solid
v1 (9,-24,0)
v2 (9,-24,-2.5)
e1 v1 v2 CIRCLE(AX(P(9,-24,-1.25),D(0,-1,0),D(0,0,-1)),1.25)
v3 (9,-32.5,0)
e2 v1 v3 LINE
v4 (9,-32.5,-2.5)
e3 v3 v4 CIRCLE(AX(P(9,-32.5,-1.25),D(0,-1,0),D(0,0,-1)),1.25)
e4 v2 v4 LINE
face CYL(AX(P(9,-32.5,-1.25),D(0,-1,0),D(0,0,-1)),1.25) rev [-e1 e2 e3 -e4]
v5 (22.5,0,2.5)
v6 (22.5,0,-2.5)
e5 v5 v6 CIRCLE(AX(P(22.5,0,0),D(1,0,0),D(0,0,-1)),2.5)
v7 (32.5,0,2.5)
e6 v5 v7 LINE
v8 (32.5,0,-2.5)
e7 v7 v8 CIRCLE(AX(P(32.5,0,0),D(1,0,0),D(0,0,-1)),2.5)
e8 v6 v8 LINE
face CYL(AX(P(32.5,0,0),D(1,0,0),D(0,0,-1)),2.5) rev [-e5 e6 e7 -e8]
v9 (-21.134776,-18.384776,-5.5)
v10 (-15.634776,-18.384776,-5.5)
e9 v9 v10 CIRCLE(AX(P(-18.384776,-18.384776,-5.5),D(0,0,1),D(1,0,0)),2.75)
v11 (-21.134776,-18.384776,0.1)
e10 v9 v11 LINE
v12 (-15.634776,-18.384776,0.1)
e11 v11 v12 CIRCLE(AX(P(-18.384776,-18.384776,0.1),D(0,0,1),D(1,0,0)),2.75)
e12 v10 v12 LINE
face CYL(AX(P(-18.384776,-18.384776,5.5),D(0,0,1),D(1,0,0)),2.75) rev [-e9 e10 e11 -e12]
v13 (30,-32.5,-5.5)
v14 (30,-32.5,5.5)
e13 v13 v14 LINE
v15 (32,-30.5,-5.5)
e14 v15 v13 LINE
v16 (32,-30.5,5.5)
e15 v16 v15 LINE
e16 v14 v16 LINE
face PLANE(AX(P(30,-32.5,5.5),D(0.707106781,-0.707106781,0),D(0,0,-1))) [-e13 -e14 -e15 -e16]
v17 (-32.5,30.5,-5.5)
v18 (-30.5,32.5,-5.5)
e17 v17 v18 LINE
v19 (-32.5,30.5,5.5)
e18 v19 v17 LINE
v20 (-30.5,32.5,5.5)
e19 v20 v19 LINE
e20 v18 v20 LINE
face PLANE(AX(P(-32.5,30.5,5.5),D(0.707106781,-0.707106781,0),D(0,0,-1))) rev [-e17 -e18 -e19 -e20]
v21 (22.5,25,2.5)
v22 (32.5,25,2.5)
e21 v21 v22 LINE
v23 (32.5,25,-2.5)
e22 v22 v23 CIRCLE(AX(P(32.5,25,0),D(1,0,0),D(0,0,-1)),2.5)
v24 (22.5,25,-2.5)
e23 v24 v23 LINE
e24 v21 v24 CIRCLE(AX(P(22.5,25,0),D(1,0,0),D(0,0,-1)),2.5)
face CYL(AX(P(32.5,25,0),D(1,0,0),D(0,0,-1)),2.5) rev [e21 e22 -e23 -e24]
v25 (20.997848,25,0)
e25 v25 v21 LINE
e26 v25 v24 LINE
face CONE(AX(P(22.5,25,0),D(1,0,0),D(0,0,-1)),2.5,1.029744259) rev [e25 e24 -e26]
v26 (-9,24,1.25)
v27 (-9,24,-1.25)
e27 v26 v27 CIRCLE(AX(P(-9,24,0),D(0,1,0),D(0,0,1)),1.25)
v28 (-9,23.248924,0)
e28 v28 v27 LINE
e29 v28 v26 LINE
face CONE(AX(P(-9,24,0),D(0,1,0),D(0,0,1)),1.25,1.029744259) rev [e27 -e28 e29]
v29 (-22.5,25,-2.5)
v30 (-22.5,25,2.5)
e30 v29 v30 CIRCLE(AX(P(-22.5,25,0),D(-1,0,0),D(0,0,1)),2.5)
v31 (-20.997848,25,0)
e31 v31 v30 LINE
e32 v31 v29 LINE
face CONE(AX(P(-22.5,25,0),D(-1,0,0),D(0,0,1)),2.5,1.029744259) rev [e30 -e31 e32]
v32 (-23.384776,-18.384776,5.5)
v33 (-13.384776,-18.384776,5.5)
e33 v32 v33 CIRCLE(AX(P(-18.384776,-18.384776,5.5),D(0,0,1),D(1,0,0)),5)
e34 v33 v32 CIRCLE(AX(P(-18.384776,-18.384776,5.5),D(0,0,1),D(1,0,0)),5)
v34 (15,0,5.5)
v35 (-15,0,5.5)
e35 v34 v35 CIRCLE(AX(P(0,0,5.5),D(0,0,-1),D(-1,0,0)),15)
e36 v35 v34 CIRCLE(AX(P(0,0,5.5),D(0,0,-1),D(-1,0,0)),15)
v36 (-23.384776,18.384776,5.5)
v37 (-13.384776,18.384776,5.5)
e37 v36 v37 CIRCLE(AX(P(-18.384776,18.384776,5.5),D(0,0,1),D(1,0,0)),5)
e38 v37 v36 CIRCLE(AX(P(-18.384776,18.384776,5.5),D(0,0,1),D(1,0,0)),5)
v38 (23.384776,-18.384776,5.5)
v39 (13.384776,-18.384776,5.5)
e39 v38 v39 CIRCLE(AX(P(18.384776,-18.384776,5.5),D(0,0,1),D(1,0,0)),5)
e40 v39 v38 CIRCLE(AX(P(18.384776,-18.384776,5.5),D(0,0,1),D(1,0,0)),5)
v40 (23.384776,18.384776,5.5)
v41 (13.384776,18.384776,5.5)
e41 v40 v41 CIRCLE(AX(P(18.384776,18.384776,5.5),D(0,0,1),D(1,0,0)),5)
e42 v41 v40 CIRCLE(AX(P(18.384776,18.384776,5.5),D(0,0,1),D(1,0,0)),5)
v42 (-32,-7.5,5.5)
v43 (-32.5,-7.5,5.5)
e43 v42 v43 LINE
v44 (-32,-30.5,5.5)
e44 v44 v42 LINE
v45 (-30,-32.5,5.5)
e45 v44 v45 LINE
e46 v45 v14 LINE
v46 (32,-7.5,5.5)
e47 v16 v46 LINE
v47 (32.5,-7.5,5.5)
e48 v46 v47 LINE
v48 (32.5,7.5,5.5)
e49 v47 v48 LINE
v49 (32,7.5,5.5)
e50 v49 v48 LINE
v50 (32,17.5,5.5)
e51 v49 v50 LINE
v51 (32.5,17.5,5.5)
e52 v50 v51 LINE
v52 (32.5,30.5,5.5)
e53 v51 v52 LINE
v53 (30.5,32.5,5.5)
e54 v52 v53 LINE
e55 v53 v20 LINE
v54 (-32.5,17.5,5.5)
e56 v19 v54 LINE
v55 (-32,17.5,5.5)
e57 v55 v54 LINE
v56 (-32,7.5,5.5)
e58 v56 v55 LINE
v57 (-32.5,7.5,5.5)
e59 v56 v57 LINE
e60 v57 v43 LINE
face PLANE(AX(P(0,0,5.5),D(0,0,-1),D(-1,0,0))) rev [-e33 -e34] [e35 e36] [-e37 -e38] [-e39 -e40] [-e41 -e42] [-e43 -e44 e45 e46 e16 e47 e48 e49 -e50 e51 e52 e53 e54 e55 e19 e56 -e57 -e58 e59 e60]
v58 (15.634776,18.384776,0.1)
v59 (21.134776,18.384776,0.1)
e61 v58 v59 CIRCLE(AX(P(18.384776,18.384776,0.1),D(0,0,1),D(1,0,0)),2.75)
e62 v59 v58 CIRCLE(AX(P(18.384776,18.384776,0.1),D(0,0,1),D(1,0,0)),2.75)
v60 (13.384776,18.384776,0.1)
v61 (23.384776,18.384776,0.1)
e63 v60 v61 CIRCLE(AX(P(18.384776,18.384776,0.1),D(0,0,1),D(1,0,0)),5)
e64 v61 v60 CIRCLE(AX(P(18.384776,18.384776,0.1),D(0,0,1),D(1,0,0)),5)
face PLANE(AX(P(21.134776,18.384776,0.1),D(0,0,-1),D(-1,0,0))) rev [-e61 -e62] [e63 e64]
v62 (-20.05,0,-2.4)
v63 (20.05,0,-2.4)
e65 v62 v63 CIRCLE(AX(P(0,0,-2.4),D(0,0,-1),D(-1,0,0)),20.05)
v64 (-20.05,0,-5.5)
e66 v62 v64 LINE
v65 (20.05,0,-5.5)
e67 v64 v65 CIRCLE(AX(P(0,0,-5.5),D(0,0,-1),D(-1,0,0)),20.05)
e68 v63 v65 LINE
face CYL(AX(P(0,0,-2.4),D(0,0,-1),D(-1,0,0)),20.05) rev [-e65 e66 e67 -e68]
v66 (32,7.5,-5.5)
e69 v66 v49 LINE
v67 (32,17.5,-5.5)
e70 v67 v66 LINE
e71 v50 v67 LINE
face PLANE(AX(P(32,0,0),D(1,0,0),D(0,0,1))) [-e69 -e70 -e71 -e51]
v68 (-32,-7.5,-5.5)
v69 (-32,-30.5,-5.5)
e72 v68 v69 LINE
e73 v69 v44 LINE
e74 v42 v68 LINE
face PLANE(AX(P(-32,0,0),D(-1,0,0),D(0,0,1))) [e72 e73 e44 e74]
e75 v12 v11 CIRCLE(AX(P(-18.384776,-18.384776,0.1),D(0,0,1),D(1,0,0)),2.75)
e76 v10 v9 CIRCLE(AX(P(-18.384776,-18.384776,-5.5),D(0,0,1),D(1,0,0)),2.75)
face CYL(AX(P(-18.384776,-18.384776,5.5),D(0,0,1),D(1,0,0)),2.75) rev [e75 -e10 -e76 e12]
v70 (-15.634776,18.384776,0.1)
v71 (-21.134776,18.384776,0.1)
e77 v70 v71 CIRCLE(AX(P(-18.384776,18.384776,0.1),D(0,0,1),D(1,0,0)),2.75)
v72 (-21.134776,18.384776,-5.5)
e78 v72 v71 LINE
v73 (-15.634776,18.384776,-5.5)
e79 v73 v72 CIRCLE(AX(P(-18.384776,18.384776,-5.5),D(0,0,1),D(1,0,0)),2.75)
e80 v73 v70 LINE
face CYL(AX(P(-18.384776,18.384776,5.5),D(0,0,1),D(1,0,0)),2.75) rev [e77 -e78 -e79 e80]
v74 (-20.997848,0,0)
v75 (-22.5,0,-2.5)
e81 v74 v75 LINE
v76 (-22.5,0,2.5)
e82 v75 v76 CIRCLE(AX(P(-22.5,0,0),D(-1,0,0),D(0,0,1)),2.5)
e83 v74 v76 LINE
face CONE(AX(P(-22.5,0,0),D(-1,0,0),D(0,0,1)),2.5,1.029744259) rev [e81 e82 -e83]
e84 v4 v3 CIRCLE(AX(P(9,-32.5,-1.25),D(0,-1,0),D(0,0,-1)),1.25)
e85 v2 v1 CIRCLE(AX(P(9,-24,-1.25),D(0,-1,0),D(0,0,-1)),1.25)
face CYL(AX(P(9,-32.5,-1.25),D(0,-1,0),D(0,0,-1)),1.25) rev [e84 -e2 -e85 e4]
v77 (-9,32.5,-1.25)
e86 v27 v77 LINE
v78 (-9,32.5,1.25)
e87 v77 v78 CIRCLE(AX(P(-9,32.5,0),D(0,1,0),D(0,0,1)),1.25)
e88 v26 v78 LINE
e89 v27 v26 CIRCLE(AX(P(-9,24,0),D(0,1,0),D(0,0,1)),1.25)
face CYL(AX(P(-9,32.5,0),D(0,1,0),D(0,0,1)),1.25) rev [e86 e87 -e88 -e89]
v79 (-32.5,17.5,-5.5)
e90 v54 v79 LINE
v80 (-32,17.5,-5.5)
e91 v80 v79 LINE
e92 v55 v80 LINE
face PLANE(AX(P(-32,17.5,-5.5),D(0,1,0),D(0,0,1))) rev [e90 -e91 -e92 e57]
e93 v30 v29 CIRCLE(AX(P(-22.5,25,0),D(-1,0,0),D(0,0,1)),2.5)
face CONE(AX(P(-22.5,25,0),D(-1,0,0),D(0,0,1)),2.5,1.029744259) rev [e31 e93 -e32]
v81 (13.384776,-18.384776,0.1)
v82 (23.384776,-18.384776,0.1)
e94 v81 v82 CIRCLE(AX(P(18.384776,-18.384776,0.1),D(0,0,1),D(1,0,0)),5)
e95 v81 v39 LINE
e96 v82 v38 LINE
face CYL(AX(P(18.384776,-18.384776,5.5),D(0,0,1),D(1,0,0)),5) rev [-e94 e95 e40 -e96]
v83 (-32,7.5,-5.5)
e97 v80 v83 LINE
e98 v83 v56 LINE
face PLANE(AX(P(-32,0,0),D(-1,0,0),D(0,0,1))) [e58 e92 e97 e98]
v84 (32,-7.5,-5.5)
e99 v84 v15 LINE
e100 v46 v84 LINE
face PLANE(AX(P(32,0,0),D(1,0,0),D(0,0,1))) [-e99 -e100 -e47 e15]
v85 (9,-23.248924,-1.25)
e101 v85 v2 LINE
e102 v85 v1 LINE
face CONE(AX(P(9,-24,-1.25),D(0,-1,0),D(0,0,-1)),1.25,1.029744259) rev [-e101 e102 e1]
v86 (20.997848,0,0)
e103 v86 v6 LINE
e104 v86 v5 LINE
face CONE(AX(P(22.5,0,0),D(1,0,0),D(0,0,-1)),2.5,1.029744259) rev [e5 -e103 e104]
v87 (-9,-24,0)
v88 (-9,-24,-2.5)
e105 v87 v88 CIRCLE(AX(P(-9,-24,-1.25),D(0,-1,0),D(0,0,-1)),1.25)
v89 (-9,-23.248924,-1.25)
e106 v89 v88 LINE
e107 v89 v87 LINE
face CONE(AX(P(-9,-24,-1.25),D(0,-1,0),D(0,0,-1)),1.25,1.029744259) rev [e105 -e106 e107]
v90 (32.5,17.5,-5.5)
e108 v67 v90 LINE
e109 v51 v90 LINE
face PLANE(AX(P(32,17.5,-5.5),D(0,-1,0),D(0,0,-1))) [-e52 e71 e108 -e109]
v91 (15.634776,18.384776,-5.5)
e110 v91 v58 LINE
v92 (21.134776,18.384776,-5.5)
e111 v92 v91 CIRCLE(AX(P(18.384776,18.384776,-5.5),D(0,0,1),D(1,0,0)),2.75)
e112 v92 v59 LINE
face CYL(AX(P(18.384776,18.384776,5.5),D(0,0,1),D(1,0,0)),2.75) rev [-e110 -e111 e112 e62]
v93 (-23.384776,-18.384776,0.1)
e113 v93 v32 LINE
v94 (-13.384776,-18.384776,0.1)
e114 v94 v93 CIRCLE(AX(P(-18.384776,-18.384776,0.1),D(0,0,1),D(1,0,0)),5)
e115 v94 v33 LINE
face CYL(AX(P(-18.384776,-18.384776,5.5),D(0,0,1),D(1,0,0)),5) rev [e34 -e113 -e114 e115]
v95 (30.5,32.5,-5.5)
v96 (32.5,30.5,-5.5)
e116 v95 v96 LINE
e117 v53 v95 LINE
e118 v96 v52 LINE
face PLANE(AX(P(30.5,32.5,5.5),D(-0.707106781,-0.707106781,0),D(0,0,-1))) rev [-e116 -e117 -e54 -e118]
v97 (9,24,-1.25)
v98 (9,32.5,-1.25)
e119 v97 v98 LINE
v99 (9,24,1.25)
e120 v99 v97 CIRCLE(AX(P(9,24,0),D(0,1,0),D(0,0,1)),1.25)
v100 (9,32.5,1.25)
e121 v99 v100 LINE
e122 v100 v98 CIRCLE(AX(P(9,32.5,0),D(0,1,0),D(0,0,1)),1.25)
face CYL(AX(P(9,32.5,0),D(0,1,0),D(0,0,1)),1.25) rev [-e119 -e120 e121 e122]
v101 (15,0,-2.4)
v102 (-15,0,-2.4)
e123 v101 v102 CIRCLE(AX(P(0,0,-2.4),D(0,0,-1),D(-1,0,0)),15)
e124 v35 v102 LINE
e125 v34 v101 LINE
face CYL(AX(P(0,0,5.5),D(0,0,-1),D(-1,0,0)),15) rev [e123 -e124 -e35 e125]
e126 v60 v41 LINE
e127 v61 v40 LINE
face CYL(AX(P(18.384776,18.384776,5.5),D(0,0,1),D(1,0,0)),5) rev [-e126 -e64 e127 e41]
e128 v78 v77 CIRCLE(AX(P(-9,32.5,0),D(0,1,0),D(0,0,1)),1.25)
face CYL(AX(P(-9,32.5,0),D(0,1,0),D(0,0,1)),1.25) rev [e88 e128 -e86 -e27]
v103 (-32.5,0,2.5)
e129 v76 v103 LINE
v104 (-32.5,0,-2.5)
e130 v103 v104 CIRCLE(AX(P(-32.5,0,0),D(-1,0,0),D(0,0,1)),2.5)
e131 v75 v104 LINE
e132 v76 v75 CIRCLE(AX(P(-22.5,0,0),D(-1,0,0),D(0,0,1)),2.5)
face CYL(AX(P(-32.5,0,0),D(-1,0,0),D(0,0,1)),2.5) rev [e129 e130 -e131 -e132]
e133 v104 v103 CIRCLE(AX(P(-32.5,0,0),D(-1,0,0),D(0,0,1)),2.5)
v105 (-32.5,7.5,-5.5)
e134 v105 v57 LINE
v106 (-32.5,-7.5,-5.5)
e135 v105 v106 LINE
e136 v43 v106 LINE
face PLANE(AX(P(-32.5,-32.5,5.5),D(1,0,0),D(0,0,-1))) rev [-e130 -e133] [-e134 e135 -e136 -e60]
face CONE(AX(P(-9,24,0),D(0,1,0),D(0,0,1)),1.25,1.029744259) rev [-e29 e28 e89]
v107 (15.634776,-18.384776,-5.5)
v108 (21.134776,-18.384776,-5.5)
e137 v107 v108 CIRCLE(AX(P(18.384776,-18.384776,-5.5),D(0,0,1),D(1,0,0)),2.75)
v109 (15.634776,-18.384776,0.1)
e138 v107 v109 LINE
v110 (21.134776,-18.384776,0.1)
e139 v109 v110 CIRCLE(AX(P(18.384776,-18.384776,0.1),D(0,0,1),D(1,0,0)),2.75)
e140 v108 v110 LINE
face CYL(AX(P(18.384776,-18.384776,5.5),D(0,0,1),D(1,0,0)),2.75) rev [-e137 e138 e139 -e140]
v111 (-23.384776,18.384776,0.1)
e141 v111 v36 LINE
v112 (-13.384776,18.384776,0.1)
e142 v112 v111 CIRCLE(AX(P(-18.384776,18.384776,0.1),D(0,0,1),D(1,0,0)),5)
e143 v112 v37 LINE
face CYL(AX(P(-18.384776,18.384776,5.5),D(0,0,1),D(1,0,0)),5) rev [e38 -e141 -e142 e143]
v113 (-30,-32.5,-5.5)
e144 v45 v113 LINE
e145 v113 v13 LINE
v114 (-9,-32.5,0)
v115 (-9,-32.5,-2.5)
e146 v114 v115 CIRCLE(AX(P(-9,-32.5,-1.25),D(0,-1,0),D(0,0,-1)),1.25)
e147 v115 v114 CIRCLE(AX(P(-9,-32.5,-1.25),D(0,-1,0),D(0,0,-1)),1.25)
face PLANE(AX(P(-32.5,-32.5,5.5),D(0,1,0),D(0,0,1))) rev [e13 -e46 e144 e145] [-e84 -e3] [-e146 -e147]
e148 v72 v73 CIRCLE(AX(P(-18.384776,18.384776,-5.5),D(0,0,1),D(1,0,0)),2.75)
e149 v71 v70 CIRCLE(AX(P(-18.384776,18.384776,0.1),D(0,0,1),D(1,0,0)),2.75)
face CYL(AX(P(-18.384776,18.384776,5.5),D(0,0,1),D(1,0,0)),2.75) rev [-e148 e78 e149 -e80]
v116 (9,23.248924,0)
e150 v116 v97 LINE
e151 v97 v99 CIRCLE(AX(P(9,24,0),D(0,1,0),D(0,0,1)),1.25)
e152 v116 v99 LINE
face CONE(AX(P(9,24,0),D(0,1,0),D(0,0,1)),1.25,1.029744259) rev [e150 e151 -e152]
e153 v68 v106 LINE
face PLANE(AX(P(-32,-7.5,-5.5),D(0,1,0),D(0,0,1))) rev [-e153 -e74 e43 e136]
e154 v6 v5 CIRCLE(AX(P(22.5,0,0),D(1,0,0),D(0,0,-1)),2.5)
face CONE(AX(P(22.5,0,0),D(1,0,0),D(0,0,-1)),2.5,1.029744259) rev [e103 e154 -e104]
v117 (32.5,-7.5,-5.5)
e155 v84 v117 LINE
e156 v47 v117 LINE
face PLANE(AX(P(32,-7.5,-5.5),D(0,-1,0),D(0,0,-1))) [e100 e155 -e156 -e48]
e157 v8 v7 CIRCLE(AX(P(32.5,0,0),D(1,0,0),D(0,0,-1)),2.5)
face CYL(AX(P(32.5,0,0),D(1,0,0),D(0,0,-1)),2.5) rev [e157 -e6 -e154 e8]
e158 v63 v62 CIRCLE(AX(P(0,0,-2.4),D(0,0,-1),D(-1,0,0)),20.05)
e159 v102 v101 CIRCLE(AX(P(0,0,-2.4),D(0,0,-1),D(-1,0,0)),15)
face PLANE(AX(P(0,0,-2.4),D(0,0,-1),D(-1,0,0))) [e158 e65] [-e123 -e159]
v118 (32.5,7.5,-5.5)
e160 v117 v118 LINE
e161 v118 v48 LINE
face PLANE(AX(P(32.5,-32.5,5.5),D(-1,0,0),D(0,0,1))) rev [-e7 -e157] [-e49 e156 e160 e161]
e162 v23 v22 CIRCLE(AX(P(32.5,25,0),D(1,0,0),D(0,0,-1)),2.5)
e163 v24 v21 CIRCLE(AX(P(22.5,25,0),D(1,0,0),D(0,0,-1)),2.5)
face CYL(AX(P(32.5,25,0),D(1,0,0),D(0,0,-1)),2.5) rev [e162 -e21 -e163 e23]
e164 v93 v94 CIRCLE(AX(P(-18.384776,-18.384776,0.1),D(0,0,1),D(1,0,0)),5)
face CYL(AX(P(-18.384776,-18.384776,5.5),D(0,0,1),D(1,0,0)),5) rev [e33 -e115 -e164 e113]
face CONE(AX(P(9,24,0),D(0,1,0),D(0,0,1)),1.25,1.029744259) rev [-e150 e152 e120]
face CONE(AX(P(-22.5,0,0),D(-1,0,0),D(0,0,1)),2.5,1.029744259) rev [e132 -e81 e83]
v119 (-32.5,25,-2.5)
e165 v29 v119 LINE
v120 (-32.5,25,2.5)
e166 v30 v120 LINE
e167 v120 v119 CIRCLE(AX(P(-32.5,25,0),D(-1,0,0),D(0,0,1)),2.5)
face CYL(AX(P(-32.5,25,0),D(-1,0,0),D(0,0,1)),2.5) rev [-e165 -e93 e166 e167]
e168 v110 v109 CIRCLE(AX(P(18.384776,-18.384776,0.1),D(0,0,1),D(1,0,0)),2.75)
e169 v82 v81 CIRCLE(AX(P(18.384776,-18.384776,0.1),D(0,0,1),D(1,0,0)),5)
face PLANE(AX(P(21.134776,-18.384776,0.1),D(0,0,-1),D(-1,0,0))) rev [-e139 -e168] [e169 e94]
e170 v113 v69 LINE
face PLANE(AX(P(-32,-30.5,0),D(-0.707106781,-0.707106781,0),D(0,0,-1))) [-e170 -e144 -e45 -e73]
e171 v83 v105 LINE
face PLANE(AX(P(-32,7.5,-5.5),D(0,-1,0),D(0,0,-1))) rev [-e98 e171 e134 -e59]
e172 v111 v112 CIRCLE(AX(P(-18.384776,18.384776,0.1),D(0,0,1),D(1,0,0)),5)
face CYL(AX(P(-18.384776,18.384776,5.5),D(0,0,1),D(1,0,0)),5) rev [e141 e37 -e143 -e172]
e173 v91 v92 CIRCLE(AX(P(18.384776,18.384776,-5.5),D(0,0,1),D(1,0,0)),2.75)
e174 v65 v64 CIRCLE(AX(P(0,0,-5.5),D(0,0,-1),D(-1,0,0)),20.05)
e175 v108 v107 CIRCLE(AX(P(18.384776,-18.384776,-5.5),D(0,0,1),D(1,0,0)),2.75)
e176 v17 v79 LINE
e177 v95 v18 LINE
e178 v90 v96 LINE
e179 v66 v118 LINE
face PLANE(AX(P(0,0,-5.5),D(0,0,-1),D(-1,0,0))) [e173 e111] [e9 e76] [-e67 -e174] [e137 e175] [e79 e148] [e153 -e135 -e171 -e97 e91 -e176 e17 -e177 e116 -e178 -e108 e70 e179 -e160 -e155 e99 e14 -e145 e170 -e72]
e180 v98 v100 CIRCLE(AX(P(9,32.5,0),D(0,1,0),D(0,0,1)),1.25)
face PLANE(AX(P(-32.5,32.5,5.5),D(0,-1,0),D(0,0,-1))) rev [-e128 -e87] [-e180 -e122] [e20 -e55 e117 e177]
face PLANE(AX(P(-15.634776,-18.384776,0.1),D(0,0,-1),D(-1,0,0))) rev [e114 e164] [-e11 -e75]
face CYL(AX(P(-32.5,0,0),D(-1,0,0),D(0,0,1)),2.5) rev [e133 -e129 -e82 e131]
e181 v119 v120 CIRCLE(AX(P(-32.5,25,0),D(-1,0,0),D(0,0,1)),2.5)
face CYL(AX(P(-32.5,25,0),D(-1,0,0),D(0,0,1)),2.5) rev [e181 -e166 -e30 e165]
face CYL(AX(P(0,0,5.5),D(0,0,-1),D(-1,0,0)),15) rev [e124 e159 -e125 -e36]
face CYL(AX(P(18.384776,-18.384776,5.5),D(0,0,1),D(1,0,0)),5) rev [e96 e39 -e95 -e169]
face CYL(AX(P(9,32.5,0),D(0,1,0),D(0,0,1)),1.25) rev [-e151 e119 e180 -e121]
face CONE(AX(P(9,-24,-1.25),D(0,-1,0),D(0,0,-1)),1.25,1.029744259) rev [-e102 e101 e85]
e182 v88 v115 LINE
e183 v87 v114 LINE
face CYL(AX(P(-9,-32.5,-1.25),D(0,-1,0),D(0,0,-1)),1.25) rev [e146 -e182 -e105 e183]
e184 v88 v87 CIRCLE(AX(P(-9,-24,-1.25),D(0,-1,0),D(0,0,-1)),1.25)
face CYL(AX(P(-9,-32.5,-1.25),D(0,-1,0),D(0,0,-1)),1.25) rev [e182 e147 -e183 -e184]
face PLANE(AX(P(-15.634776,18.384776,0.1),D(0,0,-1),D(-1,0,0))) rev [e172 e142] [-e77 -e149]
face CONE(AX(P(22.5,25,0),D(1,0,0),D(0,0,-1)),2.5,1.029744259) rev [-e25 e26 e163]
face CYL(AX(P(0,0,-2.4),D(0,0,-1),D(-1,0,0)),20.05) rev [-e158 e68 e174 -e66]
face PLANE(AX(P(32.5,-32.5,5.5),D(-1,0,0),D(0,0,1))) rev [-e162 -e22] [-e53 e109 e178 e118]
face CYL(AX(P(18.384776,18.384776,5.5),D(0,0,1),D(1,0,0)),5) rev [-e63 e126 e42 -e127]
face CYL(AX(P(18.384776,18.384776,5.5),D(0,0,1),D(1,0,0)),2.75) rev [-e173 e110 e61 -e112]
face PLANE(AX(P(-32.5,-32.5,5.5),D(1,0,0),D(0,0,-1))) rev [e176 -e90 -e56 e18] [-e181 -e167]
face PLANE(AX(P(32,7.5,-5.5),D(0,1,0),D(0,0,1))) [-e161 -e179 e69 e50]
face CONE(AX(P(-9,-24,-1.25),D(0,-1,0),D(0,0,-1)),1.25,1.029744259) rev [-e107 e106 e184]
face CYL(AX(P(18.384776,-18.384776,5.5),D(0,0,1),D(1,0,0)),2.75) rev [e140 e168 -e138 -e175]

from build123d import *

# Parameters (mm, degrees)
SKETCH_1_W                   = 65
SKETCH_1_H                   = 65
EXTRUDE_1_DEPTH              = 5.5
SKETCH_3_R                   = 20.05
CUT_EXTRUDE_1_DEPTH          = 3.1
SKETCH_4_R                   = 15
CUT_EXTRUDE_2_DEPTH          = 47.635930354
HOLE_WIZARD_M5_1_D           = 5.5
HOLE_WIZARD_M5_1_CBORE_D     = 10
HOLE_WIZARD_M5_1_CBORE_DEPTH = 5.4
HOLE_WIZARD_M6_1_AT_2_COUNT  = 2
HOLE_WIZARD_M6_1_AT_2_PITCH  = 25
SKETCH_12_W                  = 11
SKETCH_12_H                  = 10
SKETCH_12_H_2                = 25
CUT_EXTRUDE_3_DEPTH          = 0.5
CHAMFER_1_SIZE               = 2
HOLE_WIZARD_M3_2_D           = 2.5
HOLE_WIZARD_M3_2_DEPTH       = 8.5
HOLE_WIZARD_M3_2_TIP         = 0.751075774
HOLE_WIZARD_M3_3_D           = 2.5
HOLE_WIZARD_M3_3_DEPTH       = 8.5
HOLE_WIZARD_M3_3_TIP         = 0.751075774


with BuildPart() as part:
    # 草图1 → 凸台-拉伸1 (new, symmetric)
    with BuildSketch(Plane.XY):
        Rectangle(SKETCH_1_W, SKETCH_1_H)
    extrude(amount=EXTRUDE_1_DEPTH, both=True)

    # 草图3 → 切除-拉伸1 (cut)
    with BuildSketch(Plane(origin=(0, 0, -5.5), x_dir=(-1, 0, 0), z_dir=(0, 0, -1))):
        Circle(SKETCH_3_R)
    extrude(amount=-CUT_EXTRUDE_1_DEPTH, mode=Mode.SUBTRACT)

    # 草图4 → 切除-拉伸2 (cut, through all)
    with BuildSketch(Plane(origin=(0, 0, -2.4), x_dir=(-1, 0, 0), z_dir=(0, 0, -1))):
        Circle(SKETCH_4_R)
    extrude(amount=-CUT_EXTRUDE_2_DEPTH, mode=Mode.SUBTRACT)

    # M5 六角凹头螺钉的柱形沉头孔1 (through all)
    with Locations(Plane.XY.offset(5.5)):
        with Locations((-18.384776311, 18.384776311), (18.384776311, 18.384776311), (18.384776311, -18.384776311), (-18.384776311, -18.384776311)):
            CounterBoreHole(HOLE_WIZARD_M5_1_D / 2, HOLE_WIZARD_M5_1_CBORE_D / 2, HOLE_WIZARD_M5_1_CBORE_DEPTH)

    # 草图8 → M6 螺纹孔1 (revolve, cut)
    with BuildSketch(Plane(origin=(-32.5, 0, 0), x_dir=(0, 0, 1), z_dir=(0, 1, 0))):
        Polygon((0, 0), (0, 11.502151548), (2.5, 10), (2.5, 0), align=None)
    hole_wizard_m6_1 = revolve(axis=Axis((-38.85, 0, 0), (1, 0, 0)), mode=Mode.SUBTRACT)

    # M6 螺纹孔1 at 2: M6 螺纹孔1 ×2
    with Locations(*[(0, i * HOLE_WIZARD_M6_1_AT_2_PITCH, 0) for i in range(1, HOLE_WIZARD_M6_1_AT_2_COUNT)]):
        add(hole_wizard_m6_1, mode=Mode.SUBTRACT)

    # 草图12 → 切除-拉伸3 (cut)
    with BuildSketch(Plane.ZY.offset(32.5)):
        with Locations((0, 12.5)):
            Rectangle(SKETCH_12_W, SKETCH_12_H)
        with Locations((0, -20)):
            Rectangle(SKETCH_12_W, SKETCH_12_H_2)
    cut_extrude_3 = extrude(amount=-CUT_EXTRUDE_3_DEPTH, mode=Mode.SUBTRACT)

    # 镜向1: M6 螺纹孔1, 切除-拉伸3 across plane
    add(hole_wizard_m6_1.mirror(Plane(origin=(0, 0, 0), x_dir=(0, 0, 1), z_dir=(1, 0, 0))), mode=Mode.SUBTRACT)
    add(cut_extrude_3.mirror(Plane(origin=(0, 0, 0), x_dir=(0, 0, 1), z_dir=(1, 0, 0))), mode=Mode.SUBTRACT)

    # 镜向1 copy 1 sketch → 镜向1 copy 1 (revolve, cut)
    with BuildSketch(Plane(origin=(32.5, 25, 0), x_dir=(0, 0, 1), z_dir=(0, 1, 0))):
        Polygon((0, 0), (0, -11.502151548), (2.5, -10), (2.5, 0), align=None)
    revolve(axis=Axis((38.85, 25, 0), (1, 0, 0)), mode=Mode.SUBTRACT)

    # 倒角1
    chamfer_1_edges = [part.edges().sort_by_distance(p)[0] for p in [
        (32, -32.5, 0),
        (-32.5, 32.5, 0),
        (32.5, 32.5, 0),
        (-32, -32.5, 0),
    ]]
    chamfer(chamfer_1_edges, length=CHAMFER_1_SIZE)

    # M3 螺纹孔2
    with Locations(Plane(origin=(0, 32.5, 0), x_dir=(1, 0, 0), z_dir=(0, 1, 0))):
        with Locations((-9, 0), (9, 0)):
            Hole(HOLE_WIZARD_M3_2_D / 2, depth=HOLE_WIZARD_M3_2_DEPTH)
            with Locations((0, 0, -(HOLE_WIZARD_M3_2_DEPTH + HOLE_WIZARD_M3_2_TIP / 2))):  # 118° drill point
                Cone(0, HOLE_WIZARD_M3_2_D / 2, HOLE_WIZARD_M3_2_TIP, mode=Mode.SUBTRACT)

    # M3 螺纹孔3
    with Locations(Plane(origin=(0, -32.5, 0), x_dir=(-1, 0, 0), z_dir=(0, -1, 0))):
        with Locations((-9, 1.25), (9, 1.25)):
            Hole(HOLE_WIZARD_M3_3_D / 2, depth=HOLE_WIZARD_M3_3_DEPTH)
            with Locations((0, 0, -(HOLE_WIZARD_M3_3_DEPTH + HOLE_WIZARD_M3_3_TIP / 2))):  # 118° drill point
                Cone(0, HOLE_WIZARD_M3_3_D / 2, HOLE_WIZARD_M3_3_TIP, mode=Mode.SUBTRACT)


solid = part.part
